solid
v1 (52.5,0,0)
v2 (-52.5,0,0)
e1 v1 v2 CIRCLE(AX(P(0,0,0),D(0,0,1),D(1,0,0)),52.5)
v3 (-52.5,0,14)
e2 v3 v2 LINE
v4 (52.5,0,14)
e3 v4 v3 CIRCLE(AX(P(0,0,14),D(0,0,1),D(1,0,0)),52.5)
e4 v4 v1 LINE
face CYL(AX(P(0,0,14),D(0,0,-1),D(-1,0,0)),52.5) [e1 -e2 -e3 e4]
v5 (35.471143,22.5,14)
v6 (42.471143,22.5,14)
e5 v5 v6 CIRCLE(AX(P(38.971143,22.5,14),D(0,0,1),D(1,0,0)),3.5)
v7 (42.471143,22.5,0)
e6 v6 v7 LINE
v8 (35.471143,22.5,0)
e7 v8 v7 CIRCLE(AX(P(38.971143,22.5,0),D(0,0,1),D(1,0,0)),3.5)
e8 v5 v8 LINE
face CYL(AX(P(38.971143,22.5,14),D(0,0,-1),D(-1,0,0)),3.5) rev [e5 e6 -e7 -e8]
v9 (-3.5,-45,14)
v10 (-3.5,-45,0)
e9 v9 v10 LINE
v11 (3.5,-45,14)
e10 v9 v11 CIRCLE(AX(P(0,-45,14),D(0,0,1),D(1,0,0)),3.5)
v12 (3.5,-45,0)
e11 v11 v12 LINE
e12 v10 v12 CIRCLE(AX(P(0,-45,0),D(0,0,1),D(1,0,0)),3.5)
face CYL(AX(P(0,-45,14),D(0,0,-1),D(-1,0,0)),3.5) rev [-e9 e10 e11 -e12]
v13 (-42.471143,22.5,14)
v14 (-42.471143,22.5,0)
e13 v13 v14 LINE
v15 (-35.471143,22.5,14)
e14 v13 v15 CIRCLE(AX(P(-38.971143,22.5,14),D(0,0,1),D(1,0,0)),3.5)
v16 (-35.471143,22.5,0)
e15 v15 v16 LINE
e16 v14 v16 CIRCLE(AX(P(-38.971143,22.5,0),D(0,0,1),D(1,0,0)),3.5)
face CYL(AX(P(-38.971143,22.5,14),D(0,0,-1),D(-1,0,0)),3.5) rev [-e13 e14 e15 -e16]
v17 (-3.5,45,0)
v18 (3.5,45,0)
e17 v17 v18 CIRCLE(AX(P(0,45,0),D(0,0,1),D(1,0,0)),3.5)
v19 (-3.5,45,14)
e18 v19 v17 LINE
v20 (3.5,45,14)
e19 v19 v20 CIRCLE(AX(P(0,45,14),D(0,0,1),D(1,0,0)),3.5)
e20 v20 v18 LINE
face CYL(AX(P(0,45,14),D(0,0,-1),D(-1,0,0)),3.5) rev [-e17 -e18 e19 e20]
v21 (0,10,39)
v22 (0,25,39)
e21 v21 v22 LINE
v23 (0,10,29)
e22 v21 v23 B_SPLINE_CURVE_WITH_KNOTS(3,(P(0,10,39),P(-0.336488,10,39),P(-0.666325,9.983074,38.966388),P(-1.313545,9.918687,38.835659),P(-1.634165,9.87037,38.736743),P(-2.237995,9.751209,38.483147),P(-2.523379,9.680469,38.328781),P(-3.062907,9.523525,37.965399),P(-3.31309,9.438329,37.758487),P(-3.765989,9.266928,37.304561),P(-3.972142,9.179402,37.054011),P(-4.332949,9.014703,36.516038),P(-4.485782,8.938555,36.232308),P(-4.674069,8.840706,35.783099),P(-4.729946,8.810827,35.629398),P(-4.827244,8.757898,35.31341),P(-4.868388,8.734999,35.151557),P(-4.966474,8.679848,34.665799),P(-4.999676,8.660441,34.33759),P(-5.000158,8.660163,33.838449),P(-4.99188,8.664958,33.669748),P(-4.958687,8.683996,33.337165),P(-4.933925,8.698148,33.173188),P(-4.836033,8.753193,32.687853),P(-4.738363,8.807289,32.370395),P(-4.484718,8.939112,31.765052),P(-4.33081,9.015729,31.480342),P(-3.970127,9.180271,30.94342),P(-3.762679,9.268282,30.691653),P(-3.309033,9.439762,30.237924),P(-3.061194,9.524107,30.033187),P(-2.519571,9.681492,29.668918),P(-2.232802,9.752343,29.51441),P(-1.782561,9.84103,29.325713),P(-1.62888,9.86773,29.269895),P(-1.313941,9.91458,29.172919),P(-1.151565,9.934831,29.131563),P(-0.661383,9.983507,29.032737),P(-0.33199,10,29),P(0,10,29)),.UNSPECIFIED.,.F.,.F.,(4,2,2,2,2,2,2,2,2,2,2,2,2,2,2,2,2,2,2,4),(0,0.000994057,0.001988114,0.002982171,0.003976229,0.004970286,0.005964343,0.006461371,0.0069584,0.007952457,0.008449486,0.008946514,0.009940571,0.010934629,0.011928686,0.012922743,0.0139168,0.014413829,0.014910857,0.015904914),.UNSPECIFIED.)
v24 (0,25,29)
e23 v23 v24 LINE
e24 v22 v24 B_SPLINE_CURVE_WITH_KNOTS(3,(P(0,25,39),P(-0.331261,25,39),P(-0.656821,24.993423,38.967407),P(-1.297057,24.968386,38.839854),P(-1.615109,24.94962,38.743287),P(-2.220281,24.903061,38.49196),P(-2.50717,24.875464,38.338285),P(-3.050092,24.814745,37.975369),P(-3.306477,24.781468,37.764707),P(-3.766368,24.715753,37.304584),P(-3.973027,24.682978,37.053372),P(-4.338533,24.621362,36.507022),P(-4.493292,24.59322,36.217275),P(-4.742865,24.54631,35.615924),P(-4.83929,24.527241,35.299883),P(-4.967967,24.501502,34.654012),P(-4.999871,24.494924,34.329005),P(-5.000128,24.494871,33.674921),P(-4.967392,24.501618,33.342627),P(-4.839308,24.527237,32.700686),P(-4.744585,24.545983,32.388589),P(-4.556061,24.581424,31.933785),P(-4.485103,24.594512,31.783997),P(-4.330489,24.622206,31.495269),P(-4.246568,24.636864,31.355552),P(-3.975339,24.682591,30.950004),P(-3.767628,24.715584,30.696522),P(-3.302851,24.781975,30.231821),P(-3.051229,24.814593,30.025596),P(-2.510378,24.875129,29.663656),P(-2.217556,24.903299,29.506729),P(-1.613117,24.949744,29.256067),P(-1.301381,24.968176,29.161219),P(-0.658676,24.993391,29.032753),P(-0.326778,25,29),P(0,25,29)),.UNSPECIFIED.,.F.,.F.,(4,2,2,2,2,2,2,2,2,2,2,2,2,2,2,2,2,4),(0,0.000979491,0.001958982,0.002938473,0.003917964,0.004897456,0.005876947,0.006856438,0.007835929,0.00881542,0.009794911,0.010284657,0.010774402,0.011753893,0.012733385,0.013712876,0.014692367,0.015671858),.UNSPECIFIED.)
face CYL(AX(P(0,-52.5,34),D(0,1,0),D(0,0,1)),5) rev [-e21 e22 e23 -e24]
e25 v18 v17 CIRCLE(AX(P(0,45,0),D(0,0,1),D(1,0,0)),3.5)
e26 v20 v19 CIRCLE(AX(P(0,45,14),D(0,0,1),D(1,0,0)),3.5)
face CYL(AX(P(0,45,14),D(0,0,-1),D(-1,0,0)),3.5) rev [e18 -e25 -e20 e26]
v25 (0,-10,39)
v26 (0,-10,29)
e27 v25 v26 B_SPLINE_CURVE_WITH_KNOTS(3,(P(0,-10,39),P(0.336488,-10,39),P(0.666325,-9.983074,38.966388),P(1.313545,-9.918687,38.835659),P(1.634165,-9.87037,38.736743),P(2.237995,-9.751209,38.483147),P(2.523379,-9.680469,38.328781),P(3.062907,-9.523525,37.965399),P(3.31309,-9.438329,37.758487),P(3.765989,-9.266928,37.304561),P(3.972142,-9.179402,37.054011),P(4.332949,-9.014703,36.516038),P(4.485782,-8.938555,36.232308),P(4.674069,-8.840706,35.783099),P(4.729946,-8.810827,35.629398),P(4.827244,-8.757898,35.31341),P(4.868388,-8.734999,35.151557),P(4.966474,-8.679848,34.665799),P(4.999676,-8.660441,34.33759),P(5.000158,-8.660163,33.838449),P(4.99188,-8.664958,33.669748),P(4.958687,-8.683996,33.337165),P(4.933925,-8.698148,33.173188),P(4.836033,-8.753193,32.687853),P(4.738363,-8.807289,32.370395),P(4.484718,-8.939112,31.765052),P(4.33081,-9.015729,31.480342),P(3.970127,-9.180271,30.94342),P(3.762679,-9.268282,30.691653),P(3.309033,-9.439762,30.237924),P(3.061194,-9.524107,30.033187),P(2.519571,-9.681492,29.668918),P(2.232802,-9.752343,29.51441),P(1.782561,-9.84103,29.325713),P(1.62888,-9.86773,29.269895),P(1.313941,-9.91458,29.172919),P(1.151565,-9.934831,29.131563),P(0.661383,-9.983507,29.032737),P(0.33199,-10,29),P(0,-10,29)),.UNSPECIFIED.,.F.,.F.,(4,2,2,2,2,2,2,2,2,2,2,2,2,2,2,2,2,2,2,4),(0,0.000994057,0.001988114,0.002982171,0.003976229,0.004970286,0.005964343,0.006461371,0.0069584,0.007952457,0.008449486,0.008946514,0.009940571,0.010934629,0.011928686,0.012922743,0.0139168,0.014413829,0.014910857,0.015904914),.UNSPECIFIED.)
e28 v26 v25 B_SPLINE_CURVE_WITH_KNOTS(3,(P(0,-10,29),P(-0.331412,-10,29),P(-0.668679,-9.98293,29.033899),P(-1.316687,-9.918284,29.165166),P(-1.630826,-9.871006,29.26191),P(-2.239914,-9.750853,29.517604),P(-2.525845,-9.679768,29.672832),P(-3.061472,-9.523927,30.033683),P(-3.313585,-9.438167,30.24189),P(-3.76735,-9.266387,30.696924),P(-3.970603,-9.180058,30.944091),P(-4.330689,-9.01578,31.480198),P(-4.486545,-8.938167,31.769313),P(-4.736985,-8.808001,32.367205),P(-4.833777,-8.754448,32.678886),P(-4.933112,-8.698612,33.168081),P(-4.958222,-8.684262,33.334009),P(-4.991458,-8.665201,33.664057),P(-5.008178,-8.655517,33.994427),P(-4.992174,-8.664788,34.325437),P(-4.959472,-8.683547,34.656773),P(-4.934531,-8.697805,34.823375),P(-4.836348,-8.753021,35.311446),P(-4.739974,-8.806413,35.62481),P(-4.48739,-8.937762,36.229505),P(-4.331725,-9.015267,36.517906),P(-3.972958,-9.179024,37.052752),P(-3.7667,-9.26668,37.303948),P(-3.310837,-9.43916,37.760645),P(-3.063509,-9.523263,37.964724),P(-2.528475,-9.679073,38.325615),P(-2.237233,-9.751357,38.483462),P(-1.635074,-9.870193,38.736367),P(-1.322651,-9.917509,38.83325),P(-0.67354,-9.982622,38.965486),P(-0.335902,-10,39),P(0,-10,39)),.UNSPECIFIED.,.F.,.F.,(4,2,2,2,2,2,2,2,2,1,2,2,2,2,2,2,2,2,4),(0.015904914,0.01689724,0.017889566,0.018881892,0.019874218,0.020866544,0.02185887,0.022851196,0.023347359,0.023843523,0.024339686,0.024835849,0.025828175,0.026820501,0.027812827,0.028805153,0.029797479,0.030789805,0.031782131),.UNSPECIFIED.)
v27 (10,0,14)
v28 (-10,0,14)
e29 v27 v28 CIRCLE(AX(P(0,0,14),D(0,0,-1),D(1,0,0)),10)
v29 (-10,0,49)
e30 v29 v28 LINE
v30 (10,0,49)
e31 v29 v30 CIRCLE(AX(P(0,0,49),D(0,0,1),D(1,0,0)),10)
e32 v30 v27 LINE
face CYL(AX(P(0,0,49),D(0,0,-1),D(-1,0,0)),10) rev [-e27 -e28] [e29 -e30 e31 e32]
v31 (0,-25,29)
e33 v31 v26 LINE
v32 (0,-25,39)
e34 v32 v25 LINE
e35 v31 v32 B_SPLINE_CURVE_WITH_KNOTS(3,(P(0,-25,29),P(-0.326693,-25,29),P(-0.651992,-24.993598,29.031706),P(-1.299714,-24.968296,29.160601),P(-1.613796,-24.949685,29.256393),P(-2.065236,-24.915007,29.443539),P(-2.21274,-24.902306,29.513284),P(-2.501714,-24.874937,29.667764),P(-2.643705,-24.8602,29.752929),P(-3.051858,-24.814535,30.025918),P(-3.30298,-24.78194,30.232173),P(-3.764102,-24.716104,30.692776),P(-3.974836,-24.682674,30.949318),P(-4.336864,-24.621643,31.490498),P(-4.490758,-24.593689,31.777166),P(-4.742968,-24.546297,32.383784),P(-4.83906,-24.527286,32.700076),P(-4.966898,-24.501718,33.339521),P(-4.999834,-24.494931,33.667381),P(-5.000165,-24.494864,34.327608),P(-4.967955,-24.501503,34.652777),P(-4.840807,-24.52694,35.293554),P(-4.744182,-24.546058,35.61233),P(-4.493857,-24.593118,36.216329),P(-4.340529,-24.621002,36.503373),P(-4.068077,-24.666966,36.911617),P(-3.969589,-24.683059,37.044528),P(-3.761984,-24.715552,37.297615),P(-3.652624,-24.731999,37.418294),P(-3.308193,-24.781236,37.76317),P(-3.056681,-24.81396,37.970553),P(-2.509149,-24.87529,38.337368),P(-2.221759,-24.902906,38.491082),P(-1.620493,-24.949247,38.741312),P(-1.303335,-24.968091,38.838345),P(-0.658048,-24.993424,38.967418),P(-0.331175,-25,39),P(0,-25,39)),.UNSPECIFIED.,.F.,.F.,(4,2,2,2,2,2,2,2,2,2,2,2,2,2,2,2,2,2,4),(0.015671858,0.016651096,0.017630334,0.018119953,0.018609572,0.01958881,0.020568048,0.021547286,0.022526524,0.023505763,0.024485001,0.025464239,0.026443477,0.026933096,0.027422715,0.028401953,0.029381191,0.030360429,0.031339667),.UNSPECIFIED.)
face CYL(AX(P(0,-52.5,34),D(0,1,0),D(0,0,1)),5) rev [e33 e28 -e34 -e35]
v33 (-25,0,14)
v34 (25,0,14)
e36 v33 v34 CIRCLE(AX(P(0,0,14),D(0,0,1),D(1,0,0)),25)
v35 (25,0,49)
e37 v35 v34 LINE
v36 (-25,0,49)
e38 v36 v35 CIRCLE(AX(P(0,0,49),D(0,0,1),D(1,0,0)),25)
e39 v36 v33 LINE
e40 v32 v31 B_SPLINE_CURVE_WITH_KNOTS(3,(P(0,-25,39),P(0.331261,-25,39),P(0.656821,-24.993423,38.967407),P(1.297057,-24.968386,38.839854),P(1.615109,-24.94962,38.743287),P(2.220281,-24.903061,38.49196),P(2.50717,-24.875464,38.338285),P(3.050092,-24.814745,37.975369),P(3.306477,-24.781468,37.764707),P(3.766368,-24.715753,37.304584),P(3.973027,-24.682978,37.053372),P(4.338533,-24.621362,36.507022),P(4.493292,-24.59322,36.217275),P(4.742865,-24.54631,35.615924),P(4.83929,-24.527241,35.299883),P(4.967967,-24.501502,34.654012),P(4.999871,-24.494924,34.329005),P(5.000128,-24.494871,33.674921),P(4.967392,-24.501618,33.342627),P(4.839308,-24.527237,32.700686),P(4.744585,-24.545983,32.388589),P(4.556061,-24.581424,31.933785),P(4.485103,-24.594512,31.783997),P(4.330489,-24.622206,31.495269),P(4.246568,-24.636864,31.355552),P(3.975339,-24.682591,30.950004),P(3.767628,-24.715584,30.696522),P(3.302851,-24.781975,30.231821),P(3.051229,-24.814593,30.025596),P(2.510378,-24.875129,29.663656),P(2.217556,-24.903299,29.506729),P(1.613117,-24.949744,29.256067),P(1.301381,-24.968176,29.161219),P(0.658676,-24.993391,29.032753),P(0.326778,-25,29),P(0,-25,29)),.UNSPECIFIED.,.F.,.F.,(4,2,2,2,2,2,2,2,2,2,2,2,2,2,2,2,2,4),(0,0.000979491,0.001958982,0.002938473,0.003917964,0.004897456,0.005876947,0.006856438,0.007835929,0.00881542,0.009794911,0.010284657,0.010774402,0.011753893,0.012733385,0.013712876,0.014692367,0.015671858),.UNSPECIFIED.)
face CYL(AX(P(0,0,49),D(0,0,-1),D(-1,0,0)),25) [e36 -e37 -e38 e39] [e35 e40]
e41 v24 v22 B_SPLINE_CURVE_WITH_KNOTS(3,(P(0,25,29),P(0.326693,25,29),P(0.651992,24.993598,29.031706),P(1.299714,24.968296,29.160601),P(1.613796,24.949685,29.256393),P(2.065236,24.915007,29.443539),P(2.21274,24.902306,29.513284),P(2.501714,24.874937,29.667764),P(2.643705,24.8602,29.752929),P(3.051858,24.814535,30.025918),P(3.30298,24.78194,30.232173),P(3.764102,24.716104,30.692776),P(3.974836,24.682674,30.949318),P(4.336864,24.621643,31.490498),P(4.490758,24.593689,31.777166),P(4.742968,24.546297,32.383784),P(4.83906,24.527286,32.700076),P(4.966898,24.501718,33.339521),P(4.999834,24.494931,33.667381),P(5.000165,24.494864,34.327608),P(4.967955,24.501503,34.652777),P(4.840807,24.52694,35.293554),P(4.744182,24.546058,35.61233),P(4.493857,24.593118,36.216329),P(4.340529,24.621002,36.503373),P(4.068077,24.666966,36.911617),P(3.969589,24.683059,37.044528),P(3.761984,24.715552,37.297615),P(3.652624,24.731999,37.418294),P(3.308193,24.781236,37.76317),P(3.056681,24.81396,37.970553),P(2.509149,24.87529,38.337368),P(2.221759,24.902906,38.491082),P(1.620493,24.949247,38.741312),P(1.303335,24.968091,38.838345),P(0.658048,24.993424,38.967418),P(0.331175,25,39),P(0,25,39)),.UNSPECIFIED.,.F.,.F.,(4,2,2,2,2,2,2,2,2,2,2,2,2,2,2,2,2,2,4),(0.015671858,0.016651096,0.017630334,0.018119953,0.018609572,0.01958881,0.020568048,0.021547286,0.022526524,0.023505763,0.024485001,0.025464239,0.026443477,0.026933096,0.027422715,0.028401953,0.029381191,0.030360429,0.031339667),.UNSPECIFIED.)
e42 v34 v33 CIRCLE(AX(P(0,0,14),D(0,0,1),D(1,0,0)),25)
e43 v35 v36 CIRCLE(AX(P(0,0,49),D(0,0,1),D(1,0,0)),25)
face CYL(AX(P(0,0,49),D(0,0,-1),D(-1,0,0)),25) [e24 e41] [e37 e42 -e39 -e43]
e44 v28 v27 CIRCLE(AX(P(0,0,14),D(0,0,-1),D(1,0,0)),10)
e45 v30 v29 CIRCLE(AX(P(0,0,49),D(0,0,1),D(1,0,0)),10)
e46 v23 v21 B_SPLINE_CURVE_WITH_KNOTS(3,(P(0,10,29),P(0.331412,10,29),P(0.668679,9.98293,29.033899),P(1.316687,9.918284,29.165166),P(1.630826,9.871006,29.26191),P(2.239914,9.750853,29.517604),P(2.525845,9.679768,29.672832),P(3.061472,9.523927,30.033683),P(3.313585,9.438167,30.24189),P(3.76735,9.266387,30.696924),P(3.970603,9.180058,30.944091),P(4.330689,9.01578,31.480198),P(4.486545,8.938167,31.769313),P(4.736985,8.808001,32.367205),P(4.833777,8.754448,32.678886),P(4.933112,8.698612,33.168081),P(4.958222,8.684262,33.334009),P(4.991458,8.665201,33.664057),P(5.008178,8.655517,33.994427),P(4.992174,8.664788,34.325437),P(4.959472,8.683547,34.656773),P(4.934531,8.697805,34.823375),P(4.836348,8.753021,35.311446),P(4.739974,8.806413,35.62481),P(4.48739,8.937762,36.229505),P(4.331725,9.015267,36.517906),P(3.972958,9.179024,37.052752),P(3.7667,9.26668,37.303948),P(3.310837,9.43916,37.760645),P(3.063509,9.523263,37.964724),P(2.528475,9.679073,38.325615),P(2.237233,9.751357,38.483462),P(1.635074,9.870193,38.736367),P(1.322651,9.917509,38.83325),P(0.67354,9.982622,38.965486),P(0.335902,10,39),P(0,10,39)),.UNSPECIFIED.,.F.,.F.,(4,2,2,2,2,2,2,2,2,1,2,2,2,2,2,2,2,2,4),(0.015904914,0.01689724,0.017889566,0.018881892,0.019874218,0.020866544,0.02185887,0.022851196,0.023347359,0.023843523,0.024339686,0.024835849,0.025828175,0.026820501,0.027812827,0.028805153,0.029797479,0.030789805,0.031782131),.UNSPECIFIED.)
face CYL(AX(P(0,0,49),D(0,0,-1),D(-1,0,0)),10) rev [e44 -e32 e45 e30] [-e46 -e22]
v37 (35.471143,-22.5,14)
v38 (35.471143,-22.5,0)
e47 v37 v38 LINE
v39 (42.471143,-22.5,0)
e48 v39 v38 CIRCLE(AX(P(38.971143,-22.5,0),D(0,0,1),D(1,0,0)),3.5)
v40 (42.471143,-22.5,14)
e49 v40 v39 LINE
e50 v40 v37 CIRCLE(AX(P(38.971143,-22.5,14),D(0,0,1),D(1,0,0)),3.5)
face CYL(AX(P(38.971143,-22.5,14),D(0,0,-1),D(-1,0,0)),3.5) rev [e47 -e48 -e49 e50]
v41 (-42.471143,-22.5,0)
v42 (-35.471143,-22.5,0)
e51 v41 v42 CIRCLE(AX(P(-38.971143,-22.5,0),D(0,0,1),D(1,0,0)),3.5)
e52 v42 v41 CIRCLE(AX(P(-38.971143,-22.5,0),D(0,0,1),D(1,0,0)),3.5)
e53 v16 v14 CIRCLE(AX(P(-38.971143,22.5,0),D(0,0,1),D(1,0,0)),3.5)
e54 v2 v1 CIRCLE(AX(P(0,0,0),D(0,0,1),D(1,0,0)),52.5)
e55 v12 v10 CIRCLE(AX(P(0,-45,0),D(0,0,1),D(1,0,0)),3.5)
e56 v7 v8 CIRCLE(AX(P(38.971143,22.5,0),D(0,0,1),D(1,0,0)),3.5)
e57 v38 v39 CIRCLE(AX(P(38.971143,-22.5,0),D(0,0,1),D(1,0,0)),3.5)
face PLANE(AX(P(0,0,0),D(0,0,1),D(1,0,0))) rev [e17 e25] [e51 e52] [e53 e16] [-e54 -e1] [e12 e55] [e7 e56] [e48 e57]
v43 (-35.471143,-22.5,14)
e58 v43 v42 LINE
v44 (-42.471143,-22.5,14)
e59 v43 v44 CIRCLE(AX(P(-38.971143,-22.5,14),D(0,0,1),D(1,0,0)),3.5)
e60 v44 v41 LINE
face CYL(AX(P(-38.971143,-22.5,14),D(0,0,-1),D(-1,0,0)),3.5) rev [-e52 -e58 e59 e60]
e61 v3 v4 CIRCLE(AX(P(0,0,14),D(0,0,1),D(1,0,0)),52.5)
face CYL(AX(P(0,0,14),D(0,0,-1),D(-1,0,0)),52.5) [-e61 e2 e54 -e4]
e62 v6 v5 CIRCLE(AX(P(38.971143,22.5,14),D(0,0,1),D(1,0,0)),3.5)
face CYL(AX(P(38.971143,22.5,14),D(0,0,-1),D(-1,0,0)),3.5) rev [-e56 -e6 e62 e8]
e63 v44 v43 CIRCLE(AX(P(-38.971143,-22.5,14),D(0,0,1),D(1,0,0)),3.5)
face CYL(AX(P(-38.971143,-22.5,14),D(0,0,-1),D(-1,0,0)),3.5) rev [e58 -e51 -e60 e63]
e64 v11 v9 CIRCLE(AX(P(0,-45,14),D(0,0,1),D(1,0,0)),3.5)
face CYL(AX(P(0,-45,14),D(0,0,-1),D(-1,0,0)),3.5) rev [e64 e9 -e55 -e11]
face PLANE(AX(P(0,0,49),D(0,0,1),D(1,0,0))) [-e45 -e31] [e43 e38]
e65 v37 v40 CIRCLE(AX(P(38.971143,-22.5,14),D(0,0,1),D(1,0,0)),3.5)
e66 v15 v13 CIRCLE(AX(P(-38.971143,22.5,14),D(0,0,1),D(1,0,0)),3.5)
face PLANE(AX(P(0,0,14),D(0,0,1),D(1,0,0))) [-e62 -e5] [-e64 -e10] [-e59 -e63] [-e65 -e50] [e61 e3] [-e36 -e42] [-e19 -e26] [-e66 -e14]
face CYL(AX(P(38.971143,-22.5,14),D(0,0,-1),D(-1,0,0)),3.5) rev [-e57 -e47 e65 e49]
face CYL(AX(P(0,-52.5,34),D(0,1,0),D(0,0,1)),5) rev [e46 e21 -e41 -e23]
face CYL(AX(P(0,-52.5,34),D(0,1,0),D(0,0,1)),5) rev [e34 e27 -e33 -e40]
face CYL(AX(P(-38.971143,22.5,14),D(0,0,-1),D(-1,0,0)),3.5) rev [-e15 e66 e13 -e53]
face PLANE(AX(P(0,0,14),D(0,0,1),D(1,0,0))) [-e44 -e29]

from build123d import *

# Parameters (mm, degrees)
SKETCH1_R               = 52.5
SKETCH1_R_2             = 3.5
BOSS_EXTRUDE1_DEPTH     = 14
SKETCH2_R               = 25
SKETCH2_R_2             = 10
BOSS_EXTRUDE2_DEPTH     = 35
CUT_EXTRUDE1_DEPTH      = 89.95785519
CUT_EXTRUDE1_DEPTH_BACK = 89.95785519
SKETCH3_R               = 5


with BuildPart() as part:
    # Sketch1 → Boss-Extrude1 (new body)
    with BuildSketch(Plane.XY):
        Circle(SKETCH1_R)
        with Locations((0, 45)):
            Circle(SKETCH1_R_2, mode=Mode.SUBTRACT)
        with Locations((38.97114317, 22.5)):
            Circle(SKETCH1_R_2, mode=Mode.SUBTRACT)
        with Locations((38.97114317, -22.5)):
            Circle(SKETCH1_R_2, mode=Mode.SUBTRACT)
        with Locations((0, -45)):
            Circle(SKETCH1_R_2, mode=Mode.SUBTRACT)
        with Locations((-38.97114317, -22.5)):
            Circle(SKETCH1_R_2, mode=Mode.SUBTRACT)
        with Locations((-38.97114317, 22.5)):
            Circle(SKETCH1_R_2, mode=Mode.SUBTRACT)
    extrude(amount=BOSS_EXTRUDE1_DEPTH)

    # Sketch2 → Boss-Extrude2 (add)
    with BuildSketch(Plane.XY.offset(14)):
        Circle(SKETCH2_R)
        Circle(SKETCH2_R_2, mode=Mode.SUBTRACT)
    extrude(amount=BOSS_EXTRUDE2_DEPTH)

    # Sketch3 → Cut-Extrude1 (cut, two sides: drawn at the far end of the back side and taken through both)
    with BuildSketch(Plane(origin=(0, 0, 0), x_dir=(1, 0, 0), z_dir=(0, 1, 0)).offset(-CUT_EXTRUDE1_DEPTH_BACK)):
        with Locations(Location((0, -34, 0), (0, 0, 270))):
            Circle(SKETCH3_R)
    extrude(amount=CUT_EXTRUDE1_DEPTH + CUT_EXTRUDE1_DEPTH_BACK, mode=Mode.SUBTRACT)


solid = part.part
